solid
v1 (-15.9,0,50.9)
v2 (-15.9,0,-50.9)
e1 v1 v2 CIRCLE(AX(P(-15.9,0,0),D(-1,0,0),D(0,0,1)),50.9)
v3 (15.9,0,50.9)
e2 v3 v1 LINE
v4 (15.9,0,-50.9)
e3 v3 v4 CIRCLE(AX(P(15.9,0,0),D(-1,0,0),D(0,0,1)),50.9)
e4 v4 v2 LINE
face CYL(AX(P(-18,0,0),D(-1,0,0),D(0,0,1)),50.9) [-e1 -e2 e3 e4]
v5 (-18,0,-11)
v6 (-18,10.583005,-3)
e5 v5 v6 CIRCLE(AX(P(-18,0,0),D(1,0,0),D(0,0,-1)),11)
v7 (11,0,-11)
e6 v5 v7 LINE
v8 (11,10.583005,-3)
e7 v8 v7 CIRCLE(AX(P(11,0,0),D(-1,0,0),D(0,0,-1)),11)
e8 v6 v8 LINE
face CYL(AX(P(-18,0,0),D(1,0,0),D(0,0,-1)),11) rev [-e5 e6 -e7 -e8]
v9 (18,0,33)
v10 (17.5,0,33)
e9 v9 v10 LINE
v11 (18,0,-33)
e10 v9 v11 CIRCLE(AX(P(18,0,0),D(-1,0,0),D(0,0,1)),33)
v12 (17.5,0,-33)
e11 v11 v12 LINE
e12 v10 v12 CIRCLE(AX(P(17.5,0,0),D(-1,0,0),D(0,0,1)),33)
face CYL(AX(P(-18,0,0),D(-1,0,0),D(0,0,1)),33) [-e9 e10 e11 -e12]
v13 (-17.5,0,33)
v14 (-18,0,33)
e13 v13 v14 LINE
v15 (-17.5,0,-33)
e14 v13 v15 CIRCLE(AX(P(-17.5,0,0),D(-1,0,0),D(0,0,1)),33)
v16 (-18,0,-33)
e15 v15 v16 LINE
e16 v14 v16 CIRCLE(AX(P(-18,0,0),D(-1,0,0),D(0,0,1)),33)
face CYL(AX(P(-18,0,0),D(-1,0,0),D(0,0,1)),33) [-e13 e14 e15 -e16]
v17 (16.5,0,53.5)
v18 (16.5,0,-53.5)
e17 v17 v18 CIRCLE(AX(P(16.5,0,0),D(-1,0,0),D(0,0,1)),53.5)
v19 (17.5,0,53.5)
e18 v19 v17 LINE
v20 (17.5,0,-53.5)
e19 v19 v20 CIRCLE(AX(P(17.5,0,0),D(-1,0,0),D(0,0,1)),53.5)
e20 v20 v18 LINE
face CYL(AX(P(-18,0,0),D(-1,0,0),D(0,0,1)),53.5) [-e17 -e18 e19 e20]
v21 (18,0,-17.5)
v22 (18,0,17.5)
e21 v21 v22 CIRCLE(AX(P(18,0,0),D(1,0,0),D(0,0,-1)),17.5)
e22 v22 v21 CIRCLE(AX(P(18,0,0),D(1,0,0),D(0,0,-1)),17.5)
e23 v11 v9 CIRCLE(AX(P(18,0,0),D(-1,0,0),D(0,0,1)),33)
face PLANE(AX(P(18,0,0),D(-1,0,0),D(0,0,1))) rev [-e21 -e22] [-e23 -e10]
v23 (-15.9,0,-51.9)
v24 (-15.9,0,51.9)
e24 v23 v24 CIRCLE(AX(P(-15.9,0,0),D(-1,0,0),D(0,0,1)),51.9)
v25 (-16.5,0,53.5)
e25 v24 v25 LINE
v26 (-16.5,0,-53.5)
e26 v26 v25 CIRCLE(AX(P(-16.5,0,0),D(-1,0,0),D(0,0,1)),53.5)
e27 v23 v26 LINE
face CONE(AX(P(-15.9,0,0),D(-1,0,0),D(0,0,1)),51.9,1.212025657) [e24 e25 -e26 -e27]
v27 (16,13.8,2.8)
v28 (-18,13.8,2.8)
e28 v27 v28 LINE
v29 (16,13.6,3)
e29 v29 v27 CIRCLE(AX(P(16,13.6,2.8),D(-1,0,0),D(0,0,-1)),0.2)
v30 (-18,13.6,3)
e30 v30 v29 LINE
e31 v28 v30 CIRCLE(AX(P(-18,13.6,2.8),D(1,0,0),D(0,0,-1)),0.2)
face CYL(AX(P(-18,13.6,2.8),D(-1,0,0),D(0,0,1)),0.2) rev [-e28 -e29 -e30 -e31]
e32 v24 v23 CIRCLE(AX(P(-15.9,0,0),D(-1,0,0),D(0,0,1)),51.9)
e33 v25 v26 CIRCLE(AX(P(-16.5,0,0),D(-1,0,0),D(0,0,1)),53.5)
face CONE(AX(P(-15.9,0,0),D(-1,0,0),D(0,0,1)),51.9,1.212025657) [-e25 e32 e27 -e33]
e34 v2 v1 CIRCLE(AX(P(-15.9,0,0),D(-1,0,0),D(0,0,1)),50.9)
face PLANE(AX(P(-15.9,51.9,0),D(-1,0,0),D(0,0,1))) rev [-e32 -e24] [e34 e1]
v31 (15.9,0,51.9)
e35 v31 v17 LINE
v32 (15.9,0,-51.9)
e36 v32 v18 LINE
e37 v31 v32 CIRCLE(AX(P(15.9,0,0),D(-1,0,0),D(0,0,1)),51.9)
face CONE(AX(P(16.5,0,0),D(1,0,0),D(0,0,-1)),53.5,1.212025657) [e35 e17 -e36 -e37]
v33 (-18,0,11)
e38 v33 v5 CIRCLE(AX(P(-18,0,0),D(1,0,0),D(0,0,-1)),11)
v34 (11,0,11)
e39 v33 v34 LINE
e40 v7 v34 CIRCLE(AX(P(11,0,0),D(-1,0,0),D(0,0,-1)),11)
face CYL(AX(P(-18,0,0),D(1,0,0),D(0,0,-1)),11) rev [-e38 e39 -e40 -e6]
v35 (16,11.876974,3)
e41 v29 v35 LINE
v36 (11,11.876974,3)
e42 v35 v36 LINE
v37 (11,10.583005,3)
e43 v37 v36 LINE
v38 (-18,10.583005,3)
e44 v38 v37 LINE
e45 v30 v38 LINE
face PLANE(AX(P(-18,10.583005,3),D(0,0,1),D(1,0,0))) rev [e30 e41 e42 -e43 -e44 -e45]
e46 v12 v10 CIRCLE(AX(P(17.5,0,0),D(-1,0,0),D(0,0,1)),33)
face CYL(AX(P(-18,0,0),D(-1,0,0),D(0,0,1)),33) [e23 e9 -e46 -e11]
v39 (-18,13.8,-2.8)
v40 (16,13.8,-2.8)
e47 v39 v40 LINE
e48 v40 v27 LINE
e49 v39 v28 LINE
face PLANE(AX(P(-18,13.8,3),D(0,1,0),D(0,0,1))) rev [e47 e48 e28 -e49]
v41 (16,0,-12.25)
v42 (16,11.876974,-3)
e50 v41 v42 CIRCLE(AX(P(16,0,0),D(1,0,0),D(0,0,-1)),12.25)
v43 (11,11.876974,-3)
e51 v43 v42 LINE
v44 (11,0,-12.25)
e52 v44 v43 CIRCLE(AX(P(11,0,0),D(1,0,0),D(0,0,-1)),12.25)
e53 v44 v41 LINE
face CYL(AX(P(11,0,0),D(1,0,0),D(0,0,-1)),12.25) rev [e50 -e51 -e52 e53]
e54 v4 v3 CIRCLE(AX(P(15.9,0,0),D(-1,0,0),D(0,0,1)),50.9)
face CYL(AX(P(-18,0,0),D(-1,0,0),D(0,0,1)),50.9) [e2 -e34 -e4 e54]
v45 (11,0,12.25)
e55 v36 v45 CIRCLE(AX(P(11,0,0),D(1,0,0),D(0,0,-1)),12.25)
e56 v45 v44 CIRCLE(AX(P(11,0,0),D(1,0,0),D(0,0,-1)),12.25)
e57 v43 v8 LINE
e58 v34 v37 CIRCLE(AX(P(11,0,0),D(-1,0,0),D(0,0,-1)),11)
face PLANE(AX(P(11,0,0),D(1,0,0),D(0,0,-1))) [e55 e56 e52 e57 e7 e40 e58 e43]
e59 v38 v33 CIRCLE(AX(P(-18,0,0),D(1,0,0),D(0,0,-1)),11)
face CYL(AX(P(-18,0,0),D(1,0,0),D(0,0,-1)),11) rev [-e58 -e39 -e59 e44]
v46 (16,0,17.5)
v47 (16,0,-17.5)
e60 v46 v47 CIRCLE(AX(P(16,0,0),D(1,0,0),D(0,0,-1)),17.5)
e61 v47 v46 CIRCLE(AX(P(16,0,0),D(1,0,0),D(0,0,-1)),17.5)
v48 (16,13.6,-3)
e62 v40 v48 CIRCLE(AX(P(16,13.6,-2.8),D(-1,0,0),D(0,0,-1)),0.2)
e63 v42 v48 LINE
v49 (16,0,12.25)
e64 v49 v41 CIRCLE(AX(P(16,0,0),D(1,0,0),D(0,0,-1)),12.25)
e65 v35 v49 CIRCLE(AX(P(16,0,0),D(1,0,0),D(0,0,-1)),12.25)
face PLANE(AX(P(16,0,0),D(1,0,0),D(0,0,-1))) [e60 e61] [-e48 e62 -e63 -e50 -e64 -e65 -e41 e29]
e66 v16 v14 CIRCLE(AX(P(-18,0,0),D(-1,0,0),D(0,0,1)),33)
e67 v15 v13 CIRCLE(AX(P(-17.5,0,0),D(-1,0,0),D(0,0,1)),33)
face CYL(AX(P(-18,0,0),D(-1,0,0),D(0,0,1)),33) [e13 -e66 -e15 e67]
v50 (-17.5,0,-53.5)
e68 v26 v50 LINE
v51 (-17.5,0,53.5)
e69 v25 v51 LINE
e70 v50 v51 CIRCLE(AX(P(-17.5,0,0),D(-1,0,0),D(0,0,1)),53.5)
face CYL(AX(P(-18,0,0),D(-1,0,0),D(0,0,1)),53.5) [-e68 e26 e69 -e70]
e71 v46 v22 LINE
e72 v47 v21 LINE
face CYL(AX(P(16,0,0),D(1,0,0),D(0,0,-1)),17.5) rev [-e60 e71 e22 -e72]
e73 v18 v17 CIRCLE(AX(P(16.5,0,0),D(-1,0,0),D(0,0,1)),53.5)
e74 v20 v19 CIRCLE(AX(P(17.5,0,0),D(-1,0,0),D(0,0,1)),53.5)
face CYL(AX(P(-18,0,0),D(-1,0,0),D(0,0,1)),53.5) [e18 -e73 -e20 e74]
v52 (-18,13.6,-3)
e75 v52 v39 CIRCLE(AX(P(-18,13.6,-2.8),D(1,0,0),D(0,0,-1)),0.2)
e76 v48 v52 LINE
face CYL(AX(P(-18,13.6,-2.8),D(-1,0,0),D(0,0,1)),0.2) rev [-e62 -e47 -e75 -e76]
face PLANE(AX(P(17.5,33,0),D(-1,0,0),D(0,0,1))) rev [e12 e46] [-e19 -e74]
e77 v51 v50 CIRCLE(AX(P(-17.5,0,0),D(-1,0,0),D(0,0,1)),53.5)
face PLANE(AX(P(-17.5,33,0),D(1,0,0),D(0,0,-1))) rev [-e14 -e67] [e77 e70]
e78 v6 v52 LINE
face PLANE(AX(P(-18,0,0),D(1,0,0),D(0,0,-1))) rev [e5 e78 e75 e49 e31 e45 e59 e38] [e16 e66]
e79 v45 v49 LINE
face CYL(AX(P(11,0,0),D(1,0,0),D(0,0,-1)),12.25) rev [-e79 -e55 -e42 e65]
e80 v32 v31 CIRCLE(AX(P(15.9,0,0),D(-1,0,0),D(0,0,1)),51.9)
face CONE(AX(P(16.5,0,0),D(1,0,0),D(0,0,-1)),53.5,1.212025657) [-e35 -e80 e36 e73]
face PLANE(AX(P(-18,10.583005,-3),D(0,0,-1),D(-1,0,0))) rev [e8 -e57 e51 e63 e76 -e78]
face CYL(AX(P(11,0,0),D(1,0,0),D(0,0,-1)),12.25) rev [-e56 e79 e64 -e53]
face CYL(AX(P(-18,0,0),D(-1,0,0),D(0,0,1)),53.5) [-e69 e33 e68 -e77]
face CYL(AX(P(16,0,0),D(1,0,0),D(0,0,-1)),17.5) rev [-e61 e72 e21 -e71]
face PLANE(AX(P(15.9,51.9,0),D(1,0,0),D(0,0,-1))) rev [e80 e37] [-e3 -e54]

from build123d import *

# Parameters (mm, degrees)
SKETCH2_R          = 17.5
CUT_EXTRUDE1_DEPTH = 2
CUT_EXTRUDE2_DEPTH = 83.948779376
SKETCH4_R          = 12.25
CUT_EXTRUDE3_DEPTH = 5
FILLET1_R          = 0.2


with BuildPart() as part:
    # Sketch1 → Revolve1 (revolve)
    with BuildSketch(Plane.XY, mode=Mode.PRIVATE) as revolve1_sk:
        Polygon((-18, 0), (-18, 33), (-17.5, 33), (-17.5, 53.5), (-16.5, 53.5), (-15.9, 51.9), (-15.9, 50.9), (15.9, 50.9), (15.9, 51.9), (16.5, 53.5), (17.5, 53.5), (17.5, 33), (18, 33), (18, 0), align=None)
    revolve(revolve1_sk.sketch.rotate(Axis((-18, 0, 0), (1, 0, 0)), 90), axis=Axis((-18, 0, 0), (1, 0, 0)))

    # Sketch2 → Cut-Extrude1 (cut)
    with BuildSketch(Plane(origin=(18, 0, 0), x_dir=(0, 0, -1), z_dir=(1, 0, 0))):
        Circle(SKETCH2_R)
    extrude(amount=-CUT_EXTRUDE1_DEPTH, mode=Mode.SUBTRACT)

    # Sketch3 → Cut-Extrude2 (cut, through all)
    with BuildSketch(Plane(origin=(16, 0, 0), x_dir=(0, 0, -1), z_dir=(1, 0, 0))):
        with BuildLine():
            Line((3, 10.583005244), (3, 13.8))
            Line((3, 13.8), (-3, 13.8))
            Line((-3, 13.8), (-3, 10.583005244))
            ThreePointArc((-3, 10.583005244), (0, -11), (3, 10.583005244))
        make_face()
    extrude(amount=-CUT_EXTRUDE2_DEPTH, mode=Mode.SUBTRACT)

    # Sketch4 → Cut-Extrude3 (cut)
    with BuildSketch(Plane(origin=(16, 0, 0), x_dir=(0, 0, -1), z_dir=(1, 0, 0))):
        Circle(SKETCH4_R)
    extrude(amount=-CUT_EXTRUDE3_DEPTH, mode=Mode.SUBTRACT)

    # Fillet1
    fillet1_edges = [part.edges().sort_by_distance(p)[0] for p in [
        (-1, 13.8, 3),
        (-1, 13.8, -3),
    ]]
    fillet(fillet1_edges, radius=FILLET1_R)


solid = part.part
